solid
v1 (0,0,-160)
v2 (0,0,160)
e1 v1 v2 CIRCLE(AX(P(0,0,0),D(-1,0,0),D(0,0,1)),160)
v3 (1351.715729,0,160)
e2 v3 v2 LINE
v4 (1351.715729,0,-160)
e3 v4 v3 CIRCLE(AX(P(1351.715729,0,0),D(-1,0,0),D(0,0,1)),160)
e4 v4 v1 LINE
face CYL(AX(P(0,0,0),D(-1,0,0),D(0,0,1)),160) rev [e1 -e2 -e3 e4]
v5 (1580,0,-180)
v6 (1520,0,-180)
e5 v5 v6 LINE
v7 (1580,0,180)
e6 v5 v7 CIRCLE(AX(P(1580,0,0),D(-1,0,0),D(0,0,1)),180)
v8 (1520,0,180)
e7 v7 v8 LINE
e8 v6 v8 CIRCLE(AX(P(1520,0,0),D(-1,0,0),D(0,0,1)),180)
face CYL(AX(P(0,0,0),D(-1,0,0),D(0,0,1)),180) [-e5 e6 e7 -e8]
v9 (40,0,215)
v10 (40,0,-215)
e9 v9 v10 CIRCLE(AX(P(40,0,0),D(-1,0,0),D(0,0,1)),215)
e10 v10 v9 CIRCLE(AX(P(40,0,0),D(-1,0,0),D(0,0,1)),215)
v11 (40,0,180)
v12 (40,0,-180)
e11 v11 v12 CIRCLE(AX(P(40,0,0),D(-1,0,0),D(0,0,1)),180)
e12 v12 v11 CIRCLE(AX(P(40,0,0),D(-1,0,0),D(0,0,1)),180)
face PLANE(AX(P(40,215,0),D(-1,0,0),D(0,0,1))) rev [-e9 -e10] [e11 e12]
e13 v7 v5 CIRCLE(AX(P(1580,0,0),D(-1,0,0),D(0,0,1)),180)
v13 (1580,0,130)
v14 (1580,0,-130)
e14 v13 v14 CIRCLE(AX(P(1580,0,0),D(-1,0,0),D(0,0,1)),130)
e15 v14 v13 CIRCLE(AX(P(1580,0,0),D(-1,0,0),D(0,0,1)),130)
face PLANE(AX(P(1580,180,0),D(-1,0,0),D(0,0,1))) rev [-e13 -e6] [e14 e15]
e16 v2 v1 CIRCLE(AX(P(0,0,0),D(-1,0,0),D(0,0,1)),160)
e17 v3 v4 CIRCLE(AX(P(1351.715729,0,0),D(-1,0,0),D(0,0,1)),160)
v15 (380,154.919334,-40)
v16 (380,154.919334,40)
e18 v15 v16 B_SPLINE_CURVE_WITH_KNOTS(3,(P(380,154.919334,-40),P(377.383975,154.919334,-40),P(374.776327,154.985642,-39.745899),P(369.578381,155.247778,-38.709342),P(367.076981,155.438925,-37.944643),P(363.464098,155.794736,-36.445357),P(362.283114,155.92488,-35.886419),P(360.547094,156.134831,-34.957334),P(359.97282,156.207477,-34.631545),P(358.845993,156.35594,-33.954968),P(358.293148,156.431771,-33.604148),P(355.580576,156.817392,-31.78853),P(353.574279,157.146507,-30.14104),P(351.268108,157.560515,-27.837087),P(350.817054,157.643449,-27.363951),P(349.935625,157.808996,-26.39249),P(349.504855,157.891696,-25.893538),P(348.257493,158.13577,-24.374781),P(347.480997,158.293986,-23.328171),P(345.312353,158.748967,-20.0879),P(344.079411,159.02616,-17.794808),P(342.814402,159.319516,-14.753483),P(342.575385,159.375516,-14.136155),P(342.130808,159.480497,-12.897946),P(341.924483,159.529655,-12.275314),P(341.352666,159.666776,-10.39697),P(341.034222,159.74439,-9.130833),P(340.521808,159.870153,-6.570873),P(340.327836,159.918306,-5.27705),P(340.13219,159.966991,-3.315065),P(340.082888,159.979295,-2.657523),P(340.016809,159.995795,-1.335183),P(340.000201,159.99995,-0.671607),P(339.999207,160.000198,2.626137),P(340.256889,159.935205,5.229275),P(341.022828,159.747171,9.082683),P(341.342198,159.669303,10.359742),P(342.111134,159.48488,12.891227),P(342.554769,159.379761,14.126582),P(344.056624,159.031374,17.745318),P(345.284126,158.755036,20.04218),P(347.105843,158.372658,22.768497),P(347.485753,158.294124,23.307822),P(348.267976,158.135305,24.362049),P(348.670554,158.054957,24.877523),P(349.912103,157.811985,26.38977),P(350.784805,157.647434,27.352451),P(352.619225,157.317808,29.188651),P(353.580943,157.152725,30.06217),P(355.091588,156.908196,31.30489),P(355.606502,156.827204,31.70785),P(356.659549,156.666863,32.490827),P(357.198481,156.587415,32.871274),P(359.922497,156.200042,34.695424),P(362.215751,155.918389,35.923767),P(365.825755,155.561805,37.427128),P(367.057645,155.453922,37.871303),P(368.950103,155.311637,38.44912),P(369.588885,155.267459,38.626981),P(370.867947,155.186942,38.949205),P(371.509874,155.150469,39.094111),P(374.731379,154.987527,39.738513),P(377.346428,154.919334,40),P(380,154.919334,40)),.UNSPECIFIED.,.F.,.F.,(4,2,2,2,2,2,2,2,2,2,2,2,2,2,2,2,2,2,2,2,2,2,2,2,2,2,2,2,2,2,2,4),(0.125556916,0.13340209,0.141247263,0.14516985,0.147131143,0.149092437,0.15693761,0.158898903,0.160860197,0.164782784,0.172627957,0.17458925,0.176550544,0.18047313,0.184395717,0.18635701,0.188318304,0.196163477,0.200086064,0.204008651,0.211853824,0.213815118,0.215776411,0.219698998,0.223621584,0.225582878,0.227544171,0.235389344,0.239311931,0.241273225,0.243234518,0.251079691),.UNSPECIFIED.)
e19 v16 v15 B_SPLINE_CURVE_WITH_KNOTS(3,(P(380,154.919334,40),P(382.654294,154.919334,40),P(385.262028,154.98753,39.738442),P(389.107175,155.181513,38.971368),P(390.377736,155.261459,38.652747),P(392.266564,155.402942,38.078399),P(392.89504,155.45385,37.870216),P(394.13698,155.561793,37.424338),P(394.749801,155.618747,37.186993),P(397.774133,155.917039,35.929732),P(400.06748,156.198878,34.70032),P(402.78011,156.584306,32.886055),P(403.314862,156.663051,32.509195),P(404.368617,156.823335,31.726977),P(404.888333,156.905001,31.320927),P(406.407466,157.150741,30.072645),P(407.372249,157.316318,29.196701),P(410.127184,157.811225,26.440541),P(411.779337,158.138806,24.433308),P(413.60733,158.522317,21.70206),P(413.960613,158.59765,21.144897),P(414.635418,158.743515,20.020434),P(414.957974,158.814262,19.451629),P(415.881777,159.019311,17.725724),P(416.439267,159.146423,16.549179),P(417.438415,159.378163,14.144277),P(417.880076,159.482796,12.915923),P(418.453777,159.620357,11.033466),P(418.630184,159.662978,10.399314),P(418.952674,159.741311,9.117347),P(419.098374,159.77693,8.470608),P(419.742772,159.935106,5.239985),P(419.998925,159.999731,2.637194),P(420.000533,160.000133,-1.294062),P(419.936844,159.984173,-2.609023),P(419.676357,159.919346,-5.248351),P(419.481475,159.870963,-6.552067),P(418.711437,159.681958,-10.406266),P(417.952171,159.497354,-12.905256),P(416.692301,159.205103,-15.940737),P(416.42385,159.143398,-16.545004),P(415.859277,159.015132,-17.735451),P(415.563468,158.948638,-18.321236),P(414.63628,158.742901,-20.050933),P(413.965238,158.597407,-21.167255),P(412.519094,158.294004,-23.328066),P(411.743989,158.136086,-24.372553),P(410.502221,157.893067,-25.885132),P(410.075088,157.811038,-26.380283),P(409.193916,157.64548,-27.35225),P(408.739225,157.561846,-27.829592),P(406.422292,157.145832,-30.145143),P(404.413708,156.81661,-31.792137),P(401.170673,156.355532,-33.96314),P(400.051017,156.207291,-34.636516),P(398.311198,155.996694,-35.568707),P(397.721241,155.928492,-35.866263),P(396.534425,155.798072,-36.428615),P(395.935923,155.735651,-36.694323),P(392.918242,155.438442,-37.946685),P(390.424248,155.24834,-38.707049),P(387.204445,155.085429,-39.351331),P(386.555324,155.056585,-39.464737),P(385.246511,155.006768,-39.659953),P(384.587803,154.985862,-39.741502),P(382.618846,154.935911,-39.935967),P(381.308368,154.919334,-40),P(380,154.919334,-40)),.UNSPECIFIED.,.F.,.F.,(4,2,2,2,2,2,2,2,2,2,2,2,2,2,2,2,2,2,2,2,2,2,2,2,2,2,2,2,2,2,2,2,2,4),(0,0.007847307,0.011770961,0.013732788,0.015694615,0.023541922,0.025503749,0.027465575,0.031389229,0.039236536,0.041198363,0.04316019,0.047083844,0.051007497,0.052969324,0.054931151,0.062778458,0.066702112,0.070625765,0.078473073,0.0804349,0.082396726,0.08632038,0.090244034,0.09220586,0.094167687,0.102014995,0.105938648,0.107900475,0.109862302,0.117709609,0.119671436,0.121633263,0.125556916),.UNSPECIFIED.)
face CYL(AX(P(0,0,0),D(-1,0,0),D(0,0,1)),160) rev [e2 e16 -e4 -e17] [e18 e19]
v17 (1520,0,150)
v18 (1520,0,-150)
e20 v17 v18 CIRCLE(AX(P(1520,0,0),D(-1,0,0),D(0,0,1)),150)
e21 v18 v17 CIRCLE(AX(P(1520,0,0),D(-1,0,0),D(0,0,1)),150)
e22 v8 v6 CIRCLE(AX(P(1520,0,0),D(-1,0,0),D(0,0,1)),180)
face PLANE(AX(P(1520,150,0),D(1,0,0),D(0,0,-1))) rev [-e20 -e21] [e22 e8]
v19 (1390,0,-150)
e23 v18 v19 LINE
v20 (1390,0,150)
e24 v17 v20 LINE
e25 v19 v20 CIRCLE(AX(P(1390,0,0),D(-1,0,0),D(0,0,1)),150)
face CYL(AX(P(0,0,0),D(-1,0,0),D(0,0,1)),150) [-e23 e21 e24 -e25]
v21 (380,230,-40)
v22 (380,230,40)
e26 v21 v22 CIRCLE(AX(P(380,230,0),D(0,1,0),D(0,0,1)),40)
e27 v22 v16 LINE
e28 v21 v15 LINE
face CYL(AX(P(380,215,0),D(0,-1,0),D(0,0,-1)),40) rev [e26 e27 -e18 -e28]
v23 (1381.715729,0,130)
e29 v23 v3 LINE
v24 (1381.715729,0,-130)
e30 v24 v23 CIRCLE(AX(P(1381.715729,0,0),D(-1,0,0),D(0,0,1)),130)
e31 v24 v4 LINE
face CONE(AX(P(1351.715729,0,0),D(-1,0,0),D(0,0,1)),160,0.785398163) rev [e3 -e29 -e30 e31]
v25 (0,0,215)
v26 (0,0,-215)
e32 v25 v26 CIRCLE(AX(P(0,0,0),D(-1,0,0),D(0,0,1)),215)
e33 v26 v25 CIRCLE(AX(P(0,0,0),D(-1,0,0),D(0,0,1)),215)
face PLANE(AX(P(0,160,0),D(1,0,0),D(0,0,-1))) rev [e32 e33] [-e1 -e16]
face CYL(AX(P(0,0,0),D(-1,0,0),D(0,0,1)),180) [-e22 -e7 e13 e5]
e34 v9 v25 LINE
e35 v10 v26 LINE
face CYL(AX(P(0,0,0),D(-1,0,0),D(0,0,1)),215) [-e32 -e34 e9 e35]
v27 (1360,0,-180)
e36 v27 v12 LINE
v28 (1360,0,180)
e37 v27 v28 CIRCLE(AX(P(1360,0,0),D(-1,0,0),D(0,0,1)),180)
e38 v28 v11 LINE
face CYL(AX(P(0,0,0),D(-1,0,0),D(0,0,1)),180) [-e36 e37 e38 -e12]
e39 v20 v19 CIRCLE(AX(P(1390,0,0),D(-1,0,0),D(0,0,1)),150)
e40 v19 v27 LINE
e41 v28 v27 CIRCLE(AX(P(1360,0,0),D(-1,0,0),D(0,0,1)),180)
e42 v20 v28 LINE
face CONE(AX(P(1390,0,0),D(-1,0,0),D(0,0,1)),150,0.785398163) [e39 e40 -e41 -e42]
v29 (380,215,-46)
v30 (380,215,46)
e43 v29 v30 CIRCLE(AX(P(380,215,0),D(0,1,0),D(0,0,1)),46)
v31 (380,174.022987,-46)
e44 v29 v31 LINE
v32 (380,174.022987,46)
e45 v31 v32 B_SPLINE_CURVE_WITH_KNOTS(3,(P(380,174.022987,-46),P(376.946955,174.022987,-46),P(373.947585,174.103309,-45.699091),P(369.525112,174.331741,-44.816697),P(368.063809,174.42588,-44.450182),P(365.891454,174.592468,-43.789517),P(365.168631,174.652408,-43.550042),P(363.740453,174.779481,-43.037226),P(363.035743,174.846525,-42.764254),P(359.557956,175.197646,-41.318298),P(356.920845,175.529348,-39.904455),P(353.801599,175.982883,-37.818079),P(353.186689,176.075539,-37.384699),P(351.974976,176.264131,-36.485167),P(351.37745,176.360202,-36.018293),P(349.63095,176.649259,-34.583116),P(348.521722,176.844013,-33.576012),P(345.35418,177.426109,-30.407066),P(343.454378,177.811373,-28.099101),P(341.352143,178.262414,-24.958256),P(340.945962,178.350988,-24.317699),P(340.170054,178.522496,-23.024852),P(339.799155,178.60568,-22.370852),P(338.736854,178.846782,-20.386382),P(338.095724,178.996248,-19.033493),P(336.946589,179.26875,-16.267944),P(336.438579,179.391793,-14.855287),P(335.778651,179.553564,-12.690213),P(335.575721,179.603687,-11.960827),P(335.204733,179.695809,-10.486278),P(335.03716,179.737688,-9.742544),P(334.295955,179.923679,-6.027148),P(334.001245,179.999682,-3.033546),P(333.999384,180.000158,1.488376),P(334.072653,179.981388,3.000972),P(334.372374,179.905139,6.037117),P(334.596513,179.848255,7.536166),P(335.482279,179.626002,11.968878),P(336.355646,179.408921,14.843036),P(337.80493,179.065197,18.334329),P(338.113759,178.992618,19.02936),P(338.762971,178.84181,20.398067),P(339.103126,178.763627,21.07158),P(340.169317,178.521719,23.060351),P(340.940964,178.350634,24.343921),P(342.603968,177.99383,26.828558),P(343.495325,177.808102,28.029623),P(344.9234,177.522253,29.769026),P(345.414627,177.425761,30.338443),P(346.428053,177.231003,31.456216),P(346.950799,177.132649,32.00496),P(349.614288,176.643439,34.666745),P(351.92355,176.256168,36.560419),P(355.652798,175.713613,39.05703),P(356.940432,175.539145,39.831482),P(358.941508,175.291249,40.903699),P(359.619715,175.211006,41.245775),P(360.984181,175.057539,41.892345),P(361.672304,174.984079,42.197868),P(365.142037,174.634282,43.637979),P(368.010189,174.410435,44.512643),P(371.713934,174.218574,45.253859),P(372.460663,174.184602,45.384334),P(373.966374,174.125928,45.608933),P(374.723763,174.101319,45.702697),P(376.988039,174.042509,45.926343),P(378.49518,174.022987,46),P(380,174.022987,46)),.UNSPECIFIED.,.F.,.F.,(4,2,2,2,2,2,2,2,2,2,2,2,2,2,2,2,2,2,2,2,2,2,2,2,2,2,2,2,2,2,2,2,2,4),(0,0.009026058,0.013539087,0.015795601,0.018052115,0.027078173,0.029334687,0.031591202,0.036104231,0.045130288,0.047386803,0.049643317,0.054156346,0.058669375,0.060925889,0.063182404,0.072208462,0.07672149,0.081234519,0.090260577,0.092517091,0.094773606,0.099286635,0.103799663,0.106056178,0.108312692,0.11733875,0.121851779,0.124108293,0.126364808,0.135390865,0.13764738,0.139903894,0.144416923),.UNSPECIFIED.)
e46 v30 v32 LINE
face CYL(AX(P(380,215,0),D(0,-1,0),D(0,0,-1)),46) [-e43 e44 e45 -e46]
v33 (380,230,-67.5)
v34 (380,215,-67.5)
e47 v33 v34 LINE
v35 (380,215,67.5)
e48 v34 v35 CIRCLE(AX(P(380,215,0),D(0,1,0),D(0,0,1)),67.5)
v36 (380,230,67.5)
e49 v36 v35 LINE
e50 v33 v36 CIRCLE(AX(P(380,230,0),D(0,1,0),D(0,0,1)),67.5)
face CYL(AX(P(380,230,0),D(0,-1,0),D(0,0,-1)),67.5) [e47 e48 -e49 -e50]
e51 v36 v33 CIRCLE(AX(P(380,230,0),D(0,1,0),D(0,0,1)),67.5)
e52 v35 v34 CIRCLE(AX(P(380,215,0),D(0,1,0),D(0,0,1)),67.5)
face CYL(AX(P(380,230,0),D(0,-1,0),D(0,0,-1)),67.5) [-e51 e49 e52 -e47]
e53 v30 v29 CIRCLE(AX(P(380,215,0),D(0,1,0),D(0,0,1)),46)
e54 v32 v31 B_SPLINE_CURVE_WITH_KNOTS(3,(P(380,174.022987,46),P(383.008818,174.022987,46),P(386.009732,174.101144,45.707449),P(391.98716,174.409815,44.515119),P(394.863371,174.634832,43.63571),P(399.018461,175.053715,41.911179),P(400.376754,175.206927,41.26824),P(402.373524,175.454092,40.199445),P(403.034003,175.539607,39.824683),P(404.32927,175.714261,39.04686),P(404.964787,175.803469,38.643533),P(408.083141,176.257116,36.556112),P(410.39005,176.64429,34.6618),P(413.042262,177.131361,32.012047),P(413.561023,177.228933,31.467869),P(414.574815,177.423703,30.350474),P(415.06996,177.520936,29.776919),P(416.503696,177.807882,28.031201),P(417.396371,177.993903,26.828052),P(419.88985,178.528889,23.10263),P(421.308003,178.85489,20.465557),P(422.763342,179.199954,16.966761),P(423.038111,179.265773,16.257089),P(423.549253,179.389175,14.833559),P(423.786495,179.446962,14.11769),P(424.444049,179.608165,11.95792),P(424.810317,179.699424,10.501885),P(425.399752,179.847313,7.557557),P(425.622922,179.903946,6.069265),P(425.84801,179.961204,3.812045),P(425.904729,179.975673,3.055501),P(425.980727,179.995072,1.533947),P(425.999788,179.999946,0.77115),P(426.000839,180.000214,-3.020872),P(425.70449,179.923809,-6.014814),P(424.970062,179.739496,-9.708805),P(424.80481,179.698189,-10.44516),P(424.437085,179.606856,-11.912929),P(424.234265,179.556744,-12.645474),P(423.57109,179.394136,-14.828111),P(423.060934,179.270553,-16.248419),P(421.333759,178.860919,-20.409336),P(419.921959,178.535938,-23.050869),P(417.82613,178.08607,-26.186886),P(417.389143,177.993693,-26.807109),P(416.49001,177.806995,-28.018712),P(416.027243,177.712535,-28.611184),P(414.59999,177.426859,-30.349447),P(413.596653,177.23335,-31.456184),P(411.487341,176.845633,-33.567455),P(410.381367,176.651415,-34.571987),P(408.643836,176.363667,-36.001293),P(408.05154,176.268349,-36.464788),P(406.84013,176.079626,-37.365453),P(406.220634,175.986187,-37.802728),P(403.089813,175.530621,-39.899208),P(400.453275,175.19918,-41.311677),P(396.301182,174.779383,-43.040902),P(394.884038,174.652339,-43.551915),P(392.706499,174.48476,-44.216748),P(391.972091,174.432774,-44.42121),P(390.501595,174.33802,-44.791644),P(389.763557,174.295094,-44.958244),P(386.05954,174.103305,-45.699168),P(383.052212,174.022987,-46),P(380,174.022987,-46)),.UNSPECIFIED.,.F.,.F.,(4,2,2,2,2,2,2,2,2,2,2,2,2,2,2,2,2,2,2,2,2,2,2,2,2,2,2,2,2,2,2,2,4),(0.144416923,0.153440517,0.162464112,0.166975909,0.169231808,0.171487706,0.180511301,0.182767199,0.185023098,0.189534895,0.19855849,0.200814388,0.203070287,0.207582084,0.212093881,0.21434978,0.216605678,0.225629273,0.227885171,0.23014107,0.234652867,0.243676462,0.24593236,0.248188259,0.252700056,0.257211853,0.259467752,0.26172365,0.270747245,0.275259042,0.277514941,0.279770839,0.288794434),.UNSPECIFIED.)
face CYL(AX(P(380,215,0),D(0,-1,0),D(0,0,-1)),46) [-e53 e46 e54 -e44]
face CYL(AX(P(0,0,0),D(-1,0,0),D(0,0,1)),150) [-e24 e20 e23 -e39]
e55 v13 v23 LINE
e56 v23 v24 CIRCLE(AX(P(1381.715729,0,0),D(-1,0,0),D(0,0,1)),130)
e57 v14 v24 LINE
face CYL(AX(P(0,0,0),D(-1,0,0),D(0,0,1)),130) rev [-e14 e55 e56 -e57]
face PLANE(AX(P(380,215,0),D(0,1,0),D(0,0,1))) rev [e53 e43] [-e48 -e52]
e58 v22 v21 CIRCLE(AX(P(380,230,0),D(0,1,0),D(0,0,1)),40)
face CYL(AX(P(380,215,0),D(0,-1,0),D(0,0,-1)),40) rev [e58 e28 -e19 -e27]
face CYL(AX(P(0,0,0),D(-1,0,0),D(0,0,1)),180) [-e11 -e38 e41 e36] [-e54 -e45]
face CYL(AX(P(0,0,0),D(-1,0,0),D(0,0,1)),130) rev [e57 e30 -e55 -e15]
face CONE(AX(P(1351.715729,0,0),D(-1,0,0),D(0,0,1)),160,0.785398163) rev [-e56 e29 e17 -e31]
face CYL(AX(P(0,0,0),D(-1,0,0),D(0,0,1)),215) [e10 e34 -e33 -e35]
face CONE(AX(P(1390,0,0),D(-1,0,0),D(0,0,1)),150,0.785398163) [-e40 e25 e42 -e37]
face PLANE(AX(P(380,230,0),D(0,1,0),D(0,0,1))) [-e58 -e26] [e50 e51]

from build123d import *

# Parameters (mm, degrees)
SKETCH3_R           = 46
SKETCH3_R_2         = 40
BOSS_EXTRUDE1_DEPTH = 215
SKETCH4_R           = 160
CUT_EXTRUDE1_DEPTH  = 900
CUT_EXTRUDE2_START  = -300
SKETCH5_R           = 40
CUT_EXTRUDE2_DEPTH  = 300
SKETCH6_R           = 67.5
SKETCH6_R_2         = 40
BOSS_EXTRUDE2_DEPTH = 15


with BuildPart() as part:
    # Sketch1 → Revolve1 (revolve)
    with BuildSketch(Plane.XY, mode=Mode.PRIVATE) as revolve1_sk:
        Polygon((0, 160), (0, 215), (40, 215), (40, 180), (1360, 180), (1390, 150), (1520, 150), (1520, 180), (1580, 180), (1580, 130), (1381.715728753, 130), (1351.715728753, 160), align=None)
    revolve(revolve1_sk.sketch.rotate(Axis((0, 0, 0), (1, 0, 0)), 90), axis=Axis((0, 0, 0), (1, 0, 0)))

    # Sketch3 → Boss-Extrude1 (add)
    with BuildSketch(Plane(origin=(0, 0, 0), x_dir=(1, 0, 0), z_dir=(0, 1, 0))):
        with Locations(Location((380, 0, 0), (0, 0, 90))):
            Circle(SKETCH3_R)
        with Locations(Location((380, 0, 0), (0, 0, 90))):
            Circle(SKETCH3_R_2, mode=Mode.SUBTRACT)
    extrude(amount=BOSS_EXTRUDE1_DEPTH)

    # Sketch4 → Cut-Extrude1 (cut)
    with BuildSketch(Plane.ZY):
        Circle(SKETCH4_R)
    extrude(amount=-CUT_EXTRUDE1_DEPTH, mode=Mode.SUBTRACT)

    # Sketch5 → Cut-Extrude2 (cut)
    with BuildSketch(Plane(origin=(0, 215, 0), x_dir=(1, 0, 0), z_dir=(0, 1, 0)).offset(CUT_EXTRUDE2_START)):
        with Locations(Location((380, 0, 0), (0, 0, 270))):
            Circle(SKETCH5_R)
    extrude(amount=CUT_EXTRUDE2_DEPTH, mode=Mode.SUBTRACT)

    # Sketch6 → Boss-Extrude2 (add)
    with BuildSketch(Plane(origin=(0, 215, 0), x_dir=(1, 0, 0), z_dir=(0, 1, 0))):
        with Locations(Location((380, 0, 0), (0, 0, 270))):
            Circle(SKETCH6_R)
        with Locations(Location((380, 0, 0), (0, 0, 270))):
            Circle(SKETCH6_R_2, mode=Mode.SUBTRACT)
    extrude(amount=BOSS_EXTRUDE2_DEPTH)


solid = part.part
